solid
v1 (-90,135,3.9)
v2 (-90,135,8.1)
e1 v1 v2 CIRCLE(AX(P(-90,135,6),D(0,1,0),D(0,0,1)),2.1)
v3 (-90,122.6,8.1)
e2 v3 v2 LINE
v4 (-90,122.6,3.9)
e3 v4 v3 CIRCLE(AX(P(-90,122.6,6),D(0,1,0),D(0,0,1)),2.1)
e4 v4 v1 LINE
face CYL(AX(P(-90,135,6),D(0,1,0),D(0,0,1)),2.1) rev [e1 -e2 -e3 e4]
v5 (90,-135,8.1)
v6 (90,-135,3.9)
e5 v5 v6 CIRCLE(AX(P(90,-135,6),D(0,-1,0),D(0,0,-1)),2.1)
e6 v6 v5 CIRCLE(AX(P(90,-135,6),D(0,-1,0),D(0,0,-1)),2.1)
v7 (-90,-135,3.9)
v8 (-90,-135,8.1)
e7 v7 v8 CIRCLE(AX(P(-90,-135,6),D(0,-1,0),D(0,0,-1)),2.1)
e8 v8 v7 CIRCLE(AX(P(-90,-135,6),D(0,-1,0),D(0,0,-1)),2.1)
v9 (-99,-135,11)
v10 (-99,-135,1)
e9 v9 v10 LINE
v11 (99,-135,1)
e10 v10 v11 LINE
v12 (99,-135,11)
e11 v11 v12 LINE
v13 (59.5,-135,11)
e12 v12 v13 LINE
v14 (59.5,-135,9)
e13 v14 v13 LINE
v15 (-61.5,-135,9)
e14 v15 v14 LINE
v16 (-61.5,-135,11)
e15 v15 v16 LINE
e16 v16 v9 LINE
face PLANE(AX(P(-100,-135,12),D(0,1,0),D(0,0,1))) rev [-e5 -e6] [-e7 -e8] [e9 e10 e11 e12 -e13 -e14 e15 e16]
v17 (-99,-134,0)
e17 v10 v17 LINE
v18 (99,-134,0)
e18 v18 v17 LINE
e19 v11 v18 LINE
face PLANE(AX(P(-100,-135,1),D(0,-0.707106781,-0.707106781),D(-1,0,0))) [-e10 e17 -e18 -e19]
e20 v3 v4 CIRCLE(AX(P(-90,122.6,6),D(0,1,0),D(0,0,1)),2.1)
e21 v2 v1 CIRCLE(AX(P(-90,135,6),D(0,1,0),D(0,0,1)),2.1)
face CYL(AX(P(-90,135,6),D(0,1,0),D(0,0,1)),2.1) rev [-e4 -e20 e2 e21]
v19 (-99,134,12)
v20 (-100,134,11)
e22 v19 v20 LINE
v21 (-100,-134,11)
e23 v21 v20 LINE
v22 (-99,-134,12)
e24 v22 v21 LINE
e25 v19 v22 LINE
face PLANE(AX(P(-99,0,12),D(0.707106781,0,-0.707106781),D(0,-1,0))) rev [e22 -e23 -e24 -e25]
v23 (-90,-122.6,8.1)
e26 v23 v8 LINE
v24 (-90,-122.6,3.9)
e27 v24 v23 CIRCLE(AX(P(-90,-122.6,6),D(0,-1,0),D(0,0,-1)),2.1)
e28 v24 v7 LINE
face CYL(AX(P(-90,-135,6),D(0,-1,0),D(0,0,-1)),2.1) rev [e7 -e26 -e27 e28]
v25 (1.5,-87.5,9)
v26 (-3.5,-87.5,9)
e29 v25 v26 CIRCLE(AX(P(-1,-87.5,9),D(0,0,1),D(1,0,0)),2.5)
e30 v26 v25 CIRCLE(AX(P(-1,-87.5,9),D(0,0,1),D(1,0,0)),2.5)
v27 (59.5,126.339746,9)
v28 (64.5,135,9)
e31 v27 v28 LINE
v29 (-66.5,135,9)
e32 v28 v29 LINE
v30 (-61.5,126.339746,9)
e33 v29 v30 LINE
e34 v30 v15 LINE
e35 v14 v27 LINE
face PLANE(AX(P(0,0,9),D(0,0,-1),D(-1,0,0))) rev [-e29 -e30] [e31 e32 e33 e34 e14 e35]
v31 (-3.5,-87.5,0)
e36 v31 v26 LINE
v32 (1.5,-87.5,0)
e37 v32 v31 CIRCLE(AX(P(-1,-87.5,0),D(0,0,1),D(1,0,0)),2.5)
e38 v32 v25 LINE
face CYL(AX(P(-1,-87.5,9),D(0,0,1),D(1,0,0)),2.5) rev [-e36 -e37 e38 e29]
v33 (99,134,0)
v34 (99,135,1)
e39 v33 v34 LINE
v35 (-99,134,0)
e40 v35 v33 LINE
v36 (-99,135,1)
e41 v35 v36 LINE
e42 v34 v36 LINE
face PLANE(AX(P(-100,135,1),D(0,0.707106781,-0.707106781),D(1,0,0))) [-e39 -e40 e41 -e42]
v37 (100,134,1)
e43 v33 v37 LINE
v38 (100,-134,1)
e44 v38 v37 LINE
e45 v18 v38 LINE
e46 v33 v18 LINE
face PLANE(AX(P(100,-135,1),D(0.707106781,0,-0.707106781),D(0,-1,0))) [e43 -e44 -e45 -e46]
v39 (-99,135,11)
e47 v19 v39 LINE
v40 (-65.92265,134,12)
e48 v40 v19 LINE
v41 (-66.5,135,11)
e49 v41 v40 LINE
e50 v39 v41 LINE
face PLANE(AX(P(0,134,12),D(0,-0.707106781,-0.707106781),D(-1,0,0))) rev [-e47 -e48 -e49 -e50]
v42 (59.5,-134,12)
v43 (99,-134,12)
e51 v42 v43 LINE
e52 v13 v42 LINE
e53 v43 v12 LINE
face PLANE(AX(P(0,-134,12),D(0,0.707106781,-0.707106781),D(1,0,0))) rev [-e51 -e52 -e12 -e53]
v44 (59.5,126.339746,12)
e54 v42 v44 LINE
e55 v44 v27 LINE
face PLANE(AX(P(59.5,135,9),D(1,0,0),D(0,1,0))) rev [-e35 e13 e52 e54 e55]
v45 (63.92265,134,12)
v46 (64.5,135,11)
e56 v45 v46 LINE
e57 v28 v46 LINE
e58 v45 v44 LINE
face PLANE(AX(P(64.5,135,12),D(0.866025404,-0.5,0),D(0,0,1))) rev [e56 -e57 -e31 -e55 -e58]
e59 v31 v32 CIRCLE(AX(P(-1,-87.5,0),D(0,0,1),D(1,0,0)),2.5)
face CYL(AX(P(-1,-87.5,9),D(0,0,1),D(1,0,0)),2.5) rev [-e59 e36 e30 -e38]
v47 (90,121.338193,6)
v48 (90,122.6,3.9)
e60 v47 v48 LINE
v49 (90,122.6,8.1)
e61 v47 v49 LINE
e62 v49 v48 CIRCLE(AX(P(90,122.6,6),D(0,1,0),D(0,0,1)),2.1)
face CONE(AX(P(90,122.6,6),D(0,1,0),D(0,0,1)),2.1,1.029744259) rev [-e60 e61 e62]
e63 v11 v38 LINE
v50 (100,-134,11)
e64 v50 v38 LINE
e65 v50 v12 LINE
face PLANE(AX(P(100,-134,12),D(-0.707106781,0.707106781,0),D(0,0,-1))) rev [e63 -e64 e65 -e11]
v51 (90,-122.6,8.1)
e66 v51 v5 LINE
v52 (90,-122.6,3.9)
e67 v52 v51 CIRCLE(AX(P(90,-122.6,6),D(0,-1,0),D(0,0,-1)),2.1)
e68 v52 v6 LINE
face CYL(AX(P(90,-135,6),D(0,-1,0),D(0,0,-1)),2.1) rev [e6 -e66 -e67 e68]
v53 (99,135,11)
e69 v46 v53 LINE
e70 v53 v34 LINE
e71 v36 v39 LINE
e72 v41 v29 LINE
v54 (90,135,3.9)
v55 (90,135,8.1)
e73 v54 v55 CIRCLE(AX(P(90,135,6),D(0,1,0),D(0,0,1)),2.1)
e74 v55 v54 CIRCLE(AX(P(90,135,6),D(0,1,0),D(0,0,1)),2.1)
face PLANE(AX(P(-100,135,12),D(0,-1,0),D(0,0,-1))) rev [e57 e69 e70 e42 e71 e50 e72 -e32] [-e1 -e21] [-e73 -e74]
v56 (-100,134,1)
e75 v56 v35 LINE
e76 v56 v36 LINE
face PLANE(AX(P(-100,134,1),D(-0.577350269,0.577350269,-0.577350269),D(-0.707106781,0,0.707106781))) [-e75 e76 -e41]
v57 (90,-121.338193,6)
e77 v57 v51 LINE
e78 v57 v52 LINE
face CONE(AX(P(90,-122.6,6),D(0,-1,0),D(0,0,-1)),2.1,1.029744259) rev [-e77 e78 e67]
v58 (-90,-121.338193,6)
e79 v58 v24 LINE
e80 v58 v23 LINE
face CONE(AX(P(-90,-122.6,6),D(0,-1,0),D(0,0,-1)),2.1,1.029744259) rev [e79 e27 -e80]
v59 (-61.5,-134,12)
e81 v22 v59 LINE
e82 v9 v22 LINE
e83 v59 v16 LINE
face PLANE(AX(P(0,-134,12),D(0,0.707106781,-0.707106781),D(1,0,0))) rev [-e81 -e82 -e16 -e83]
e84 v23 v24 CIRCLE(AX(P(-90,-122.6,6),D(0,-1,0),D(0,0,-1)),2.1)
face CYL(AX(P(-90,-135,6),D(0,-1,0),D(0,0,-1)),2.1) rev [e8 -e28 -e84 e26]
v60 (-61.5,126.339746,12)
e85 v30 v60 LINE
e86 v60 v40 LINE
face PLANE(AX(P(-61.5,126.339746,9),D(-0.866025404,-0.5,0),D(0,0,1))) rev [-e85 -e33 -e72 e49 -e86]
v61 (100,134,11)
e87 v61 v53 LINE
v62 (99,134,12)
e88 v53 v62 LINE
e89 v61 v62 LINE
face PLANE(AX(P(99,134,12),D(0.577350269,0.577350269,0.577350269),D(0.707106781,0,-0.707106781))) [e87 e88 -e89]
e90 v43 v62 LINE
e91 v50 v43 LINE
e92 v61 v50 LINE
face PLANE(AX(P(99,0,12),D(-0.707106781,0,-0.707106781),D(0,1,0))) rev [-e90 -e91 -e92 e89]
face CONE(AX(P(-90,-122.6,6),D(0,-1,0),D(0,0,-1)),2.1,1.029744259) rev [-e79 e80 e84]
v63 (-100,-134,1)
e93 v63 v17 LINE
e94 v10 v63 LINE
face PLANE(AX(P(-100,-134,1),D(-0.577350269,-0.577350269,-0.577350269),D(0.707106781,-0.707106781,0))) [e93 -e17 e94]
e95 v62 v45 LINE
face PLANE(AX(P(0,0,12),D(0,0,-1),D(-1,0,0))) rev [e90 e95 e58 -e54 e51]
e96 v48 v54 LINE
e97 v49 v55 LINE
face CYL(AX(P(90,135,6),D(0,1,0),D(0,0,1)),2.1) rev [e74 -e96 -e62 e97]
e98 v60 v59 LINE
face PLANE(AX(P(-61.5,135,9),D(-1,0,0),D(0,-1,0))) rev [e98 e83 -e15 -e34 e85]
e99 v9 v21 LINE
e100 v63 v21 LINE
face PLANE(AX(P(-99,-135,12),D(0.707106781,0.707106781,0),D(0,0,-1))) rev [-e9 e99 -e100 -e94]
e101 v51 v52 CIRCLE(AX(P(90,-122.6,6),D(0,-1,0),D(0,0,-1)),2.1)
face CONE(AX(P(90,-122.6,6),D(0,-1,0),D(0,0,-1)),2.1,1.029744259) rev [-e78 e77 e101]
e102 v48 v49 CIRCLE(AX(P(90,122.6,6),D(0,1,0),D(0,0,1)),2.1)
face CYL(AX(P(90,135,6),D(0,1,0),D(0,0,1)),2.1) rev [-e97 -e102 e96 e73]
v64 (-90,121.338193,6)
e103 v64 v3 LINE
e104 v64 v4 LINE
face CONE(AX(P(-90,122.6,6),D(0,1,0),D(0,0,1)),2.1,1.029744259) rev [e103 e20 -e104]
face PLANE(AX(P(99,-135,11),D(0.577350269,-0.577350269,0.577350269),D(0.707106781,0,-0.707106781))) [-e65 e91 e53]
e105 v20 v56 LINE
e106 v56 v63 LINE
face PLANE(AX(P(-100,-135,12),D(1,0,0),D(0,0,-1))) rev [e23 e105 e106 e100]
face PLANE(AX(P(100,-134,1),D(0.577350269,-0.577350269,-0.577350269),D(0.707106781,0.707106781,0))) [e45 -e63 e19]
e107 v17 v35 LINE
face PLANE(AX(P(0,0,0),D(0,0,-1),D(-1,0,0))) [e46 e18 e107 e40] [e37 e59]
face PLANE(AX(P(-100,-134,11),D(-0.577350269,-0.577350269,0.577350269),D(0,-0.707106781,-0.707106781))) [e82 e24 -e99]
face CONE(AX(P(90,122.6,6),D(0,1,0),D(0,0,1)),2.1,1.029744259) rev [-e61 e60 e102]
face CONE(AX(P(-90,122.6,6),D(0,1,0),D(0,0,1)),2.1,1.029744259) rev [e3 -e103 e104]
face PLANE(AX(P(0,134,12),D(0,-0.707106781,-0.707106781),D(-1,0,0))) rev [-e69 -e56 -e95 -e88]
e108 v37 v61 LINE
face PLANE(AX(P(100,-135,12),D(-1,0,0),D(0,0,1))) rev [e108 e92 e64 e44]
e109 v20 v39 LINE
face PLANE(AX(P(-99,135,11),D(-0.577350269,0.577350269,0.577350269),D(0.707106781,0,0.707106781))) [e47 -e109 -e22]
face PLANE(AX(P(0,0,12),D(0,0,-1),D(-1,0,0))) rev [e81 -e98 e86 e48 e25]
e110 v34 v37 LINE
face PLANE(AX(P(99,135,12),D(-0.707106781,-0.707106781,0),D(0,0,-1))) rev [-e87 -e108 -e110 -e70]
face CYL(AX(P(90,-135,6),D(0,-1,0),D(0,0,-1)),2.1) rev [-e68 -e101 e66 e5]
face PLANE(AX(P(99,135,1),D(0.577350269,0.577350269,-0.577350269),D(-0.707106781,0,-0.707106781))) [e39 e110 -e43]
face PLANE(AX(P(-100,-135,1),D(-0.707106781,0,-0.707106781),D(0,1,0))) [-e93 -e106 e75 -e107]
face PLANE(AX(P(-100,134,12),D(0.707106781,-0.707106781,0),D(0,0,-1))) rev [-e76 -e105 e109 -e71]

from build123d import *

# Parameters (mm, degrees)
SKETCH_1_W                  = 200
SKETCH_1_H                  = 270
EXTRUDE_1_DEPTH             = 12
SKETCH_2_W                  = 121
SKETCH_2_H                  = 270
CUT_EXTRUDE_1_DEPTH         = 3
CHAMFER_1_SIZE              = 5
CHAMFER_1_SIZE2             = 8.660254038
HOLE_WIZARD_M5_1_AT_2_COUNT = 2
HOLE_WIZARD_M5_1_AT_2_PITCH = 180
CHAMFER_2_SIZE              = 1
MM_1_D                      = 5


with BuildPart() as part:
    # 草图1 → 凸台-拉伸1 (new body)
    with BuildSketch(Plane.XY):
        Rectangle(SKETCH_1_W, SKETCH_1_H)
    extrude(amount=EXTRUDE_1_DEPTH)

    # 草图2 → 切除-拉伸1 (cut)
    with BuildSketch(Plane.XY.offset(12)):
        with Locations((-1, 0)):
            Rectangle(SKETCH_2_W, SKETCH_2_H)
    extrude(amount=-CUT_EXTRUDE_1_DEPTH, mode=Mode.SUBTRACT)

    # 倒角1
    chamfer_1_edges = [part.edges().sort_by_distance(p)[0] for p in [
        (59.5, 135, 10.5),
        (-61.5, 135, 10.5),
    ]]
    chamfer_1_side = [part.faces().sort_by_distance(p)[0] for p in [
        (0.17820324, 135, 5.19808542),
    ]]
    chamfer(chamfer_1_edges, length=CHAMFER_1_SIZE, length2=CHAMFER_1_SIZE2, reference=chamfer_1_side[0])

    # 草图4 → M5 螺纹孔1 (revolve, cut)
    with BuildSketch(Plane(origin=(90, 135, 6), x_dir=(0, 0, 1), z_dir=(1, 0, 0))):
        Polygon((0, 0), (0, 13.6618073), (2.1, 12.4), (2.1, 0), align=None)
    hole_wizard_m5_1 = revolve(axis=Axis((90, 141.35, 6), (0, -1, 0)), mode=Mode.SUBTRACT)

    # M5 螺纹孔1 at 2: M5 螺纹孔1 ×2
    with Locations(*[(-i * HOLE_WIZARD_M5_1_AT_2_PITCH, 0, 0) for i in range(1, HOLE_WIZARD_M5_1_AT_2_COUNT)]):
        add(hole_wizard_m5_1, mode=Mode.SUBTRACT)

    # 镜向1: M5 螺纹孔1 across plane
    add(hole_wizard_m5_1.mirror(Plane.ZX), mode=Mode.SUBTRACT)

    # 镜向1 copy 1 sketch → 镜向1 copy 1 (revolve, cut)
    with BuildSketch(Plane(origin=(-90, -135, 6), x_dir=(0, 0, 1), z_dir=(1, 0, 0))):
        Polygon((0, 0), (0, -13.6618073), (2.1, -12.4), (2.1, 0), align=None)
    revolve(axis=Axis((-90, -141.35, 6), (0, -1, 0)), mode=Mode.SUBTRACT)

    # 倒角2
    chamfer_2_edges = [part.edges().sort_by_distance(p)[0] for p in [
        (-100, 0, 12),
        (-80.75, -135, 12),
        (79.75, -135, 12),
        (-83.25, 135, 12),
        (100, 0, 12),
        (0, -135, 0),
        (-100, 0, 0),
        (0, 135, 0),
        (100, 0, 0),
        (82.25, 135, 12),
        (100, -135, 6),
        (-100, -135, 6),
        (-100, 135, 6),
        (100, 135, 6),
    ]]
    chamfer(chamfer_2_edges, length=CHAMFER_2_SIZE)

    # 大小mm 暗销孔1 (through all)
    with Locations(Plane.XY.offset(9)):
        with Locations((-1, -87.5)):
            Hole(MM_1_D / 2)


solid = part.part
